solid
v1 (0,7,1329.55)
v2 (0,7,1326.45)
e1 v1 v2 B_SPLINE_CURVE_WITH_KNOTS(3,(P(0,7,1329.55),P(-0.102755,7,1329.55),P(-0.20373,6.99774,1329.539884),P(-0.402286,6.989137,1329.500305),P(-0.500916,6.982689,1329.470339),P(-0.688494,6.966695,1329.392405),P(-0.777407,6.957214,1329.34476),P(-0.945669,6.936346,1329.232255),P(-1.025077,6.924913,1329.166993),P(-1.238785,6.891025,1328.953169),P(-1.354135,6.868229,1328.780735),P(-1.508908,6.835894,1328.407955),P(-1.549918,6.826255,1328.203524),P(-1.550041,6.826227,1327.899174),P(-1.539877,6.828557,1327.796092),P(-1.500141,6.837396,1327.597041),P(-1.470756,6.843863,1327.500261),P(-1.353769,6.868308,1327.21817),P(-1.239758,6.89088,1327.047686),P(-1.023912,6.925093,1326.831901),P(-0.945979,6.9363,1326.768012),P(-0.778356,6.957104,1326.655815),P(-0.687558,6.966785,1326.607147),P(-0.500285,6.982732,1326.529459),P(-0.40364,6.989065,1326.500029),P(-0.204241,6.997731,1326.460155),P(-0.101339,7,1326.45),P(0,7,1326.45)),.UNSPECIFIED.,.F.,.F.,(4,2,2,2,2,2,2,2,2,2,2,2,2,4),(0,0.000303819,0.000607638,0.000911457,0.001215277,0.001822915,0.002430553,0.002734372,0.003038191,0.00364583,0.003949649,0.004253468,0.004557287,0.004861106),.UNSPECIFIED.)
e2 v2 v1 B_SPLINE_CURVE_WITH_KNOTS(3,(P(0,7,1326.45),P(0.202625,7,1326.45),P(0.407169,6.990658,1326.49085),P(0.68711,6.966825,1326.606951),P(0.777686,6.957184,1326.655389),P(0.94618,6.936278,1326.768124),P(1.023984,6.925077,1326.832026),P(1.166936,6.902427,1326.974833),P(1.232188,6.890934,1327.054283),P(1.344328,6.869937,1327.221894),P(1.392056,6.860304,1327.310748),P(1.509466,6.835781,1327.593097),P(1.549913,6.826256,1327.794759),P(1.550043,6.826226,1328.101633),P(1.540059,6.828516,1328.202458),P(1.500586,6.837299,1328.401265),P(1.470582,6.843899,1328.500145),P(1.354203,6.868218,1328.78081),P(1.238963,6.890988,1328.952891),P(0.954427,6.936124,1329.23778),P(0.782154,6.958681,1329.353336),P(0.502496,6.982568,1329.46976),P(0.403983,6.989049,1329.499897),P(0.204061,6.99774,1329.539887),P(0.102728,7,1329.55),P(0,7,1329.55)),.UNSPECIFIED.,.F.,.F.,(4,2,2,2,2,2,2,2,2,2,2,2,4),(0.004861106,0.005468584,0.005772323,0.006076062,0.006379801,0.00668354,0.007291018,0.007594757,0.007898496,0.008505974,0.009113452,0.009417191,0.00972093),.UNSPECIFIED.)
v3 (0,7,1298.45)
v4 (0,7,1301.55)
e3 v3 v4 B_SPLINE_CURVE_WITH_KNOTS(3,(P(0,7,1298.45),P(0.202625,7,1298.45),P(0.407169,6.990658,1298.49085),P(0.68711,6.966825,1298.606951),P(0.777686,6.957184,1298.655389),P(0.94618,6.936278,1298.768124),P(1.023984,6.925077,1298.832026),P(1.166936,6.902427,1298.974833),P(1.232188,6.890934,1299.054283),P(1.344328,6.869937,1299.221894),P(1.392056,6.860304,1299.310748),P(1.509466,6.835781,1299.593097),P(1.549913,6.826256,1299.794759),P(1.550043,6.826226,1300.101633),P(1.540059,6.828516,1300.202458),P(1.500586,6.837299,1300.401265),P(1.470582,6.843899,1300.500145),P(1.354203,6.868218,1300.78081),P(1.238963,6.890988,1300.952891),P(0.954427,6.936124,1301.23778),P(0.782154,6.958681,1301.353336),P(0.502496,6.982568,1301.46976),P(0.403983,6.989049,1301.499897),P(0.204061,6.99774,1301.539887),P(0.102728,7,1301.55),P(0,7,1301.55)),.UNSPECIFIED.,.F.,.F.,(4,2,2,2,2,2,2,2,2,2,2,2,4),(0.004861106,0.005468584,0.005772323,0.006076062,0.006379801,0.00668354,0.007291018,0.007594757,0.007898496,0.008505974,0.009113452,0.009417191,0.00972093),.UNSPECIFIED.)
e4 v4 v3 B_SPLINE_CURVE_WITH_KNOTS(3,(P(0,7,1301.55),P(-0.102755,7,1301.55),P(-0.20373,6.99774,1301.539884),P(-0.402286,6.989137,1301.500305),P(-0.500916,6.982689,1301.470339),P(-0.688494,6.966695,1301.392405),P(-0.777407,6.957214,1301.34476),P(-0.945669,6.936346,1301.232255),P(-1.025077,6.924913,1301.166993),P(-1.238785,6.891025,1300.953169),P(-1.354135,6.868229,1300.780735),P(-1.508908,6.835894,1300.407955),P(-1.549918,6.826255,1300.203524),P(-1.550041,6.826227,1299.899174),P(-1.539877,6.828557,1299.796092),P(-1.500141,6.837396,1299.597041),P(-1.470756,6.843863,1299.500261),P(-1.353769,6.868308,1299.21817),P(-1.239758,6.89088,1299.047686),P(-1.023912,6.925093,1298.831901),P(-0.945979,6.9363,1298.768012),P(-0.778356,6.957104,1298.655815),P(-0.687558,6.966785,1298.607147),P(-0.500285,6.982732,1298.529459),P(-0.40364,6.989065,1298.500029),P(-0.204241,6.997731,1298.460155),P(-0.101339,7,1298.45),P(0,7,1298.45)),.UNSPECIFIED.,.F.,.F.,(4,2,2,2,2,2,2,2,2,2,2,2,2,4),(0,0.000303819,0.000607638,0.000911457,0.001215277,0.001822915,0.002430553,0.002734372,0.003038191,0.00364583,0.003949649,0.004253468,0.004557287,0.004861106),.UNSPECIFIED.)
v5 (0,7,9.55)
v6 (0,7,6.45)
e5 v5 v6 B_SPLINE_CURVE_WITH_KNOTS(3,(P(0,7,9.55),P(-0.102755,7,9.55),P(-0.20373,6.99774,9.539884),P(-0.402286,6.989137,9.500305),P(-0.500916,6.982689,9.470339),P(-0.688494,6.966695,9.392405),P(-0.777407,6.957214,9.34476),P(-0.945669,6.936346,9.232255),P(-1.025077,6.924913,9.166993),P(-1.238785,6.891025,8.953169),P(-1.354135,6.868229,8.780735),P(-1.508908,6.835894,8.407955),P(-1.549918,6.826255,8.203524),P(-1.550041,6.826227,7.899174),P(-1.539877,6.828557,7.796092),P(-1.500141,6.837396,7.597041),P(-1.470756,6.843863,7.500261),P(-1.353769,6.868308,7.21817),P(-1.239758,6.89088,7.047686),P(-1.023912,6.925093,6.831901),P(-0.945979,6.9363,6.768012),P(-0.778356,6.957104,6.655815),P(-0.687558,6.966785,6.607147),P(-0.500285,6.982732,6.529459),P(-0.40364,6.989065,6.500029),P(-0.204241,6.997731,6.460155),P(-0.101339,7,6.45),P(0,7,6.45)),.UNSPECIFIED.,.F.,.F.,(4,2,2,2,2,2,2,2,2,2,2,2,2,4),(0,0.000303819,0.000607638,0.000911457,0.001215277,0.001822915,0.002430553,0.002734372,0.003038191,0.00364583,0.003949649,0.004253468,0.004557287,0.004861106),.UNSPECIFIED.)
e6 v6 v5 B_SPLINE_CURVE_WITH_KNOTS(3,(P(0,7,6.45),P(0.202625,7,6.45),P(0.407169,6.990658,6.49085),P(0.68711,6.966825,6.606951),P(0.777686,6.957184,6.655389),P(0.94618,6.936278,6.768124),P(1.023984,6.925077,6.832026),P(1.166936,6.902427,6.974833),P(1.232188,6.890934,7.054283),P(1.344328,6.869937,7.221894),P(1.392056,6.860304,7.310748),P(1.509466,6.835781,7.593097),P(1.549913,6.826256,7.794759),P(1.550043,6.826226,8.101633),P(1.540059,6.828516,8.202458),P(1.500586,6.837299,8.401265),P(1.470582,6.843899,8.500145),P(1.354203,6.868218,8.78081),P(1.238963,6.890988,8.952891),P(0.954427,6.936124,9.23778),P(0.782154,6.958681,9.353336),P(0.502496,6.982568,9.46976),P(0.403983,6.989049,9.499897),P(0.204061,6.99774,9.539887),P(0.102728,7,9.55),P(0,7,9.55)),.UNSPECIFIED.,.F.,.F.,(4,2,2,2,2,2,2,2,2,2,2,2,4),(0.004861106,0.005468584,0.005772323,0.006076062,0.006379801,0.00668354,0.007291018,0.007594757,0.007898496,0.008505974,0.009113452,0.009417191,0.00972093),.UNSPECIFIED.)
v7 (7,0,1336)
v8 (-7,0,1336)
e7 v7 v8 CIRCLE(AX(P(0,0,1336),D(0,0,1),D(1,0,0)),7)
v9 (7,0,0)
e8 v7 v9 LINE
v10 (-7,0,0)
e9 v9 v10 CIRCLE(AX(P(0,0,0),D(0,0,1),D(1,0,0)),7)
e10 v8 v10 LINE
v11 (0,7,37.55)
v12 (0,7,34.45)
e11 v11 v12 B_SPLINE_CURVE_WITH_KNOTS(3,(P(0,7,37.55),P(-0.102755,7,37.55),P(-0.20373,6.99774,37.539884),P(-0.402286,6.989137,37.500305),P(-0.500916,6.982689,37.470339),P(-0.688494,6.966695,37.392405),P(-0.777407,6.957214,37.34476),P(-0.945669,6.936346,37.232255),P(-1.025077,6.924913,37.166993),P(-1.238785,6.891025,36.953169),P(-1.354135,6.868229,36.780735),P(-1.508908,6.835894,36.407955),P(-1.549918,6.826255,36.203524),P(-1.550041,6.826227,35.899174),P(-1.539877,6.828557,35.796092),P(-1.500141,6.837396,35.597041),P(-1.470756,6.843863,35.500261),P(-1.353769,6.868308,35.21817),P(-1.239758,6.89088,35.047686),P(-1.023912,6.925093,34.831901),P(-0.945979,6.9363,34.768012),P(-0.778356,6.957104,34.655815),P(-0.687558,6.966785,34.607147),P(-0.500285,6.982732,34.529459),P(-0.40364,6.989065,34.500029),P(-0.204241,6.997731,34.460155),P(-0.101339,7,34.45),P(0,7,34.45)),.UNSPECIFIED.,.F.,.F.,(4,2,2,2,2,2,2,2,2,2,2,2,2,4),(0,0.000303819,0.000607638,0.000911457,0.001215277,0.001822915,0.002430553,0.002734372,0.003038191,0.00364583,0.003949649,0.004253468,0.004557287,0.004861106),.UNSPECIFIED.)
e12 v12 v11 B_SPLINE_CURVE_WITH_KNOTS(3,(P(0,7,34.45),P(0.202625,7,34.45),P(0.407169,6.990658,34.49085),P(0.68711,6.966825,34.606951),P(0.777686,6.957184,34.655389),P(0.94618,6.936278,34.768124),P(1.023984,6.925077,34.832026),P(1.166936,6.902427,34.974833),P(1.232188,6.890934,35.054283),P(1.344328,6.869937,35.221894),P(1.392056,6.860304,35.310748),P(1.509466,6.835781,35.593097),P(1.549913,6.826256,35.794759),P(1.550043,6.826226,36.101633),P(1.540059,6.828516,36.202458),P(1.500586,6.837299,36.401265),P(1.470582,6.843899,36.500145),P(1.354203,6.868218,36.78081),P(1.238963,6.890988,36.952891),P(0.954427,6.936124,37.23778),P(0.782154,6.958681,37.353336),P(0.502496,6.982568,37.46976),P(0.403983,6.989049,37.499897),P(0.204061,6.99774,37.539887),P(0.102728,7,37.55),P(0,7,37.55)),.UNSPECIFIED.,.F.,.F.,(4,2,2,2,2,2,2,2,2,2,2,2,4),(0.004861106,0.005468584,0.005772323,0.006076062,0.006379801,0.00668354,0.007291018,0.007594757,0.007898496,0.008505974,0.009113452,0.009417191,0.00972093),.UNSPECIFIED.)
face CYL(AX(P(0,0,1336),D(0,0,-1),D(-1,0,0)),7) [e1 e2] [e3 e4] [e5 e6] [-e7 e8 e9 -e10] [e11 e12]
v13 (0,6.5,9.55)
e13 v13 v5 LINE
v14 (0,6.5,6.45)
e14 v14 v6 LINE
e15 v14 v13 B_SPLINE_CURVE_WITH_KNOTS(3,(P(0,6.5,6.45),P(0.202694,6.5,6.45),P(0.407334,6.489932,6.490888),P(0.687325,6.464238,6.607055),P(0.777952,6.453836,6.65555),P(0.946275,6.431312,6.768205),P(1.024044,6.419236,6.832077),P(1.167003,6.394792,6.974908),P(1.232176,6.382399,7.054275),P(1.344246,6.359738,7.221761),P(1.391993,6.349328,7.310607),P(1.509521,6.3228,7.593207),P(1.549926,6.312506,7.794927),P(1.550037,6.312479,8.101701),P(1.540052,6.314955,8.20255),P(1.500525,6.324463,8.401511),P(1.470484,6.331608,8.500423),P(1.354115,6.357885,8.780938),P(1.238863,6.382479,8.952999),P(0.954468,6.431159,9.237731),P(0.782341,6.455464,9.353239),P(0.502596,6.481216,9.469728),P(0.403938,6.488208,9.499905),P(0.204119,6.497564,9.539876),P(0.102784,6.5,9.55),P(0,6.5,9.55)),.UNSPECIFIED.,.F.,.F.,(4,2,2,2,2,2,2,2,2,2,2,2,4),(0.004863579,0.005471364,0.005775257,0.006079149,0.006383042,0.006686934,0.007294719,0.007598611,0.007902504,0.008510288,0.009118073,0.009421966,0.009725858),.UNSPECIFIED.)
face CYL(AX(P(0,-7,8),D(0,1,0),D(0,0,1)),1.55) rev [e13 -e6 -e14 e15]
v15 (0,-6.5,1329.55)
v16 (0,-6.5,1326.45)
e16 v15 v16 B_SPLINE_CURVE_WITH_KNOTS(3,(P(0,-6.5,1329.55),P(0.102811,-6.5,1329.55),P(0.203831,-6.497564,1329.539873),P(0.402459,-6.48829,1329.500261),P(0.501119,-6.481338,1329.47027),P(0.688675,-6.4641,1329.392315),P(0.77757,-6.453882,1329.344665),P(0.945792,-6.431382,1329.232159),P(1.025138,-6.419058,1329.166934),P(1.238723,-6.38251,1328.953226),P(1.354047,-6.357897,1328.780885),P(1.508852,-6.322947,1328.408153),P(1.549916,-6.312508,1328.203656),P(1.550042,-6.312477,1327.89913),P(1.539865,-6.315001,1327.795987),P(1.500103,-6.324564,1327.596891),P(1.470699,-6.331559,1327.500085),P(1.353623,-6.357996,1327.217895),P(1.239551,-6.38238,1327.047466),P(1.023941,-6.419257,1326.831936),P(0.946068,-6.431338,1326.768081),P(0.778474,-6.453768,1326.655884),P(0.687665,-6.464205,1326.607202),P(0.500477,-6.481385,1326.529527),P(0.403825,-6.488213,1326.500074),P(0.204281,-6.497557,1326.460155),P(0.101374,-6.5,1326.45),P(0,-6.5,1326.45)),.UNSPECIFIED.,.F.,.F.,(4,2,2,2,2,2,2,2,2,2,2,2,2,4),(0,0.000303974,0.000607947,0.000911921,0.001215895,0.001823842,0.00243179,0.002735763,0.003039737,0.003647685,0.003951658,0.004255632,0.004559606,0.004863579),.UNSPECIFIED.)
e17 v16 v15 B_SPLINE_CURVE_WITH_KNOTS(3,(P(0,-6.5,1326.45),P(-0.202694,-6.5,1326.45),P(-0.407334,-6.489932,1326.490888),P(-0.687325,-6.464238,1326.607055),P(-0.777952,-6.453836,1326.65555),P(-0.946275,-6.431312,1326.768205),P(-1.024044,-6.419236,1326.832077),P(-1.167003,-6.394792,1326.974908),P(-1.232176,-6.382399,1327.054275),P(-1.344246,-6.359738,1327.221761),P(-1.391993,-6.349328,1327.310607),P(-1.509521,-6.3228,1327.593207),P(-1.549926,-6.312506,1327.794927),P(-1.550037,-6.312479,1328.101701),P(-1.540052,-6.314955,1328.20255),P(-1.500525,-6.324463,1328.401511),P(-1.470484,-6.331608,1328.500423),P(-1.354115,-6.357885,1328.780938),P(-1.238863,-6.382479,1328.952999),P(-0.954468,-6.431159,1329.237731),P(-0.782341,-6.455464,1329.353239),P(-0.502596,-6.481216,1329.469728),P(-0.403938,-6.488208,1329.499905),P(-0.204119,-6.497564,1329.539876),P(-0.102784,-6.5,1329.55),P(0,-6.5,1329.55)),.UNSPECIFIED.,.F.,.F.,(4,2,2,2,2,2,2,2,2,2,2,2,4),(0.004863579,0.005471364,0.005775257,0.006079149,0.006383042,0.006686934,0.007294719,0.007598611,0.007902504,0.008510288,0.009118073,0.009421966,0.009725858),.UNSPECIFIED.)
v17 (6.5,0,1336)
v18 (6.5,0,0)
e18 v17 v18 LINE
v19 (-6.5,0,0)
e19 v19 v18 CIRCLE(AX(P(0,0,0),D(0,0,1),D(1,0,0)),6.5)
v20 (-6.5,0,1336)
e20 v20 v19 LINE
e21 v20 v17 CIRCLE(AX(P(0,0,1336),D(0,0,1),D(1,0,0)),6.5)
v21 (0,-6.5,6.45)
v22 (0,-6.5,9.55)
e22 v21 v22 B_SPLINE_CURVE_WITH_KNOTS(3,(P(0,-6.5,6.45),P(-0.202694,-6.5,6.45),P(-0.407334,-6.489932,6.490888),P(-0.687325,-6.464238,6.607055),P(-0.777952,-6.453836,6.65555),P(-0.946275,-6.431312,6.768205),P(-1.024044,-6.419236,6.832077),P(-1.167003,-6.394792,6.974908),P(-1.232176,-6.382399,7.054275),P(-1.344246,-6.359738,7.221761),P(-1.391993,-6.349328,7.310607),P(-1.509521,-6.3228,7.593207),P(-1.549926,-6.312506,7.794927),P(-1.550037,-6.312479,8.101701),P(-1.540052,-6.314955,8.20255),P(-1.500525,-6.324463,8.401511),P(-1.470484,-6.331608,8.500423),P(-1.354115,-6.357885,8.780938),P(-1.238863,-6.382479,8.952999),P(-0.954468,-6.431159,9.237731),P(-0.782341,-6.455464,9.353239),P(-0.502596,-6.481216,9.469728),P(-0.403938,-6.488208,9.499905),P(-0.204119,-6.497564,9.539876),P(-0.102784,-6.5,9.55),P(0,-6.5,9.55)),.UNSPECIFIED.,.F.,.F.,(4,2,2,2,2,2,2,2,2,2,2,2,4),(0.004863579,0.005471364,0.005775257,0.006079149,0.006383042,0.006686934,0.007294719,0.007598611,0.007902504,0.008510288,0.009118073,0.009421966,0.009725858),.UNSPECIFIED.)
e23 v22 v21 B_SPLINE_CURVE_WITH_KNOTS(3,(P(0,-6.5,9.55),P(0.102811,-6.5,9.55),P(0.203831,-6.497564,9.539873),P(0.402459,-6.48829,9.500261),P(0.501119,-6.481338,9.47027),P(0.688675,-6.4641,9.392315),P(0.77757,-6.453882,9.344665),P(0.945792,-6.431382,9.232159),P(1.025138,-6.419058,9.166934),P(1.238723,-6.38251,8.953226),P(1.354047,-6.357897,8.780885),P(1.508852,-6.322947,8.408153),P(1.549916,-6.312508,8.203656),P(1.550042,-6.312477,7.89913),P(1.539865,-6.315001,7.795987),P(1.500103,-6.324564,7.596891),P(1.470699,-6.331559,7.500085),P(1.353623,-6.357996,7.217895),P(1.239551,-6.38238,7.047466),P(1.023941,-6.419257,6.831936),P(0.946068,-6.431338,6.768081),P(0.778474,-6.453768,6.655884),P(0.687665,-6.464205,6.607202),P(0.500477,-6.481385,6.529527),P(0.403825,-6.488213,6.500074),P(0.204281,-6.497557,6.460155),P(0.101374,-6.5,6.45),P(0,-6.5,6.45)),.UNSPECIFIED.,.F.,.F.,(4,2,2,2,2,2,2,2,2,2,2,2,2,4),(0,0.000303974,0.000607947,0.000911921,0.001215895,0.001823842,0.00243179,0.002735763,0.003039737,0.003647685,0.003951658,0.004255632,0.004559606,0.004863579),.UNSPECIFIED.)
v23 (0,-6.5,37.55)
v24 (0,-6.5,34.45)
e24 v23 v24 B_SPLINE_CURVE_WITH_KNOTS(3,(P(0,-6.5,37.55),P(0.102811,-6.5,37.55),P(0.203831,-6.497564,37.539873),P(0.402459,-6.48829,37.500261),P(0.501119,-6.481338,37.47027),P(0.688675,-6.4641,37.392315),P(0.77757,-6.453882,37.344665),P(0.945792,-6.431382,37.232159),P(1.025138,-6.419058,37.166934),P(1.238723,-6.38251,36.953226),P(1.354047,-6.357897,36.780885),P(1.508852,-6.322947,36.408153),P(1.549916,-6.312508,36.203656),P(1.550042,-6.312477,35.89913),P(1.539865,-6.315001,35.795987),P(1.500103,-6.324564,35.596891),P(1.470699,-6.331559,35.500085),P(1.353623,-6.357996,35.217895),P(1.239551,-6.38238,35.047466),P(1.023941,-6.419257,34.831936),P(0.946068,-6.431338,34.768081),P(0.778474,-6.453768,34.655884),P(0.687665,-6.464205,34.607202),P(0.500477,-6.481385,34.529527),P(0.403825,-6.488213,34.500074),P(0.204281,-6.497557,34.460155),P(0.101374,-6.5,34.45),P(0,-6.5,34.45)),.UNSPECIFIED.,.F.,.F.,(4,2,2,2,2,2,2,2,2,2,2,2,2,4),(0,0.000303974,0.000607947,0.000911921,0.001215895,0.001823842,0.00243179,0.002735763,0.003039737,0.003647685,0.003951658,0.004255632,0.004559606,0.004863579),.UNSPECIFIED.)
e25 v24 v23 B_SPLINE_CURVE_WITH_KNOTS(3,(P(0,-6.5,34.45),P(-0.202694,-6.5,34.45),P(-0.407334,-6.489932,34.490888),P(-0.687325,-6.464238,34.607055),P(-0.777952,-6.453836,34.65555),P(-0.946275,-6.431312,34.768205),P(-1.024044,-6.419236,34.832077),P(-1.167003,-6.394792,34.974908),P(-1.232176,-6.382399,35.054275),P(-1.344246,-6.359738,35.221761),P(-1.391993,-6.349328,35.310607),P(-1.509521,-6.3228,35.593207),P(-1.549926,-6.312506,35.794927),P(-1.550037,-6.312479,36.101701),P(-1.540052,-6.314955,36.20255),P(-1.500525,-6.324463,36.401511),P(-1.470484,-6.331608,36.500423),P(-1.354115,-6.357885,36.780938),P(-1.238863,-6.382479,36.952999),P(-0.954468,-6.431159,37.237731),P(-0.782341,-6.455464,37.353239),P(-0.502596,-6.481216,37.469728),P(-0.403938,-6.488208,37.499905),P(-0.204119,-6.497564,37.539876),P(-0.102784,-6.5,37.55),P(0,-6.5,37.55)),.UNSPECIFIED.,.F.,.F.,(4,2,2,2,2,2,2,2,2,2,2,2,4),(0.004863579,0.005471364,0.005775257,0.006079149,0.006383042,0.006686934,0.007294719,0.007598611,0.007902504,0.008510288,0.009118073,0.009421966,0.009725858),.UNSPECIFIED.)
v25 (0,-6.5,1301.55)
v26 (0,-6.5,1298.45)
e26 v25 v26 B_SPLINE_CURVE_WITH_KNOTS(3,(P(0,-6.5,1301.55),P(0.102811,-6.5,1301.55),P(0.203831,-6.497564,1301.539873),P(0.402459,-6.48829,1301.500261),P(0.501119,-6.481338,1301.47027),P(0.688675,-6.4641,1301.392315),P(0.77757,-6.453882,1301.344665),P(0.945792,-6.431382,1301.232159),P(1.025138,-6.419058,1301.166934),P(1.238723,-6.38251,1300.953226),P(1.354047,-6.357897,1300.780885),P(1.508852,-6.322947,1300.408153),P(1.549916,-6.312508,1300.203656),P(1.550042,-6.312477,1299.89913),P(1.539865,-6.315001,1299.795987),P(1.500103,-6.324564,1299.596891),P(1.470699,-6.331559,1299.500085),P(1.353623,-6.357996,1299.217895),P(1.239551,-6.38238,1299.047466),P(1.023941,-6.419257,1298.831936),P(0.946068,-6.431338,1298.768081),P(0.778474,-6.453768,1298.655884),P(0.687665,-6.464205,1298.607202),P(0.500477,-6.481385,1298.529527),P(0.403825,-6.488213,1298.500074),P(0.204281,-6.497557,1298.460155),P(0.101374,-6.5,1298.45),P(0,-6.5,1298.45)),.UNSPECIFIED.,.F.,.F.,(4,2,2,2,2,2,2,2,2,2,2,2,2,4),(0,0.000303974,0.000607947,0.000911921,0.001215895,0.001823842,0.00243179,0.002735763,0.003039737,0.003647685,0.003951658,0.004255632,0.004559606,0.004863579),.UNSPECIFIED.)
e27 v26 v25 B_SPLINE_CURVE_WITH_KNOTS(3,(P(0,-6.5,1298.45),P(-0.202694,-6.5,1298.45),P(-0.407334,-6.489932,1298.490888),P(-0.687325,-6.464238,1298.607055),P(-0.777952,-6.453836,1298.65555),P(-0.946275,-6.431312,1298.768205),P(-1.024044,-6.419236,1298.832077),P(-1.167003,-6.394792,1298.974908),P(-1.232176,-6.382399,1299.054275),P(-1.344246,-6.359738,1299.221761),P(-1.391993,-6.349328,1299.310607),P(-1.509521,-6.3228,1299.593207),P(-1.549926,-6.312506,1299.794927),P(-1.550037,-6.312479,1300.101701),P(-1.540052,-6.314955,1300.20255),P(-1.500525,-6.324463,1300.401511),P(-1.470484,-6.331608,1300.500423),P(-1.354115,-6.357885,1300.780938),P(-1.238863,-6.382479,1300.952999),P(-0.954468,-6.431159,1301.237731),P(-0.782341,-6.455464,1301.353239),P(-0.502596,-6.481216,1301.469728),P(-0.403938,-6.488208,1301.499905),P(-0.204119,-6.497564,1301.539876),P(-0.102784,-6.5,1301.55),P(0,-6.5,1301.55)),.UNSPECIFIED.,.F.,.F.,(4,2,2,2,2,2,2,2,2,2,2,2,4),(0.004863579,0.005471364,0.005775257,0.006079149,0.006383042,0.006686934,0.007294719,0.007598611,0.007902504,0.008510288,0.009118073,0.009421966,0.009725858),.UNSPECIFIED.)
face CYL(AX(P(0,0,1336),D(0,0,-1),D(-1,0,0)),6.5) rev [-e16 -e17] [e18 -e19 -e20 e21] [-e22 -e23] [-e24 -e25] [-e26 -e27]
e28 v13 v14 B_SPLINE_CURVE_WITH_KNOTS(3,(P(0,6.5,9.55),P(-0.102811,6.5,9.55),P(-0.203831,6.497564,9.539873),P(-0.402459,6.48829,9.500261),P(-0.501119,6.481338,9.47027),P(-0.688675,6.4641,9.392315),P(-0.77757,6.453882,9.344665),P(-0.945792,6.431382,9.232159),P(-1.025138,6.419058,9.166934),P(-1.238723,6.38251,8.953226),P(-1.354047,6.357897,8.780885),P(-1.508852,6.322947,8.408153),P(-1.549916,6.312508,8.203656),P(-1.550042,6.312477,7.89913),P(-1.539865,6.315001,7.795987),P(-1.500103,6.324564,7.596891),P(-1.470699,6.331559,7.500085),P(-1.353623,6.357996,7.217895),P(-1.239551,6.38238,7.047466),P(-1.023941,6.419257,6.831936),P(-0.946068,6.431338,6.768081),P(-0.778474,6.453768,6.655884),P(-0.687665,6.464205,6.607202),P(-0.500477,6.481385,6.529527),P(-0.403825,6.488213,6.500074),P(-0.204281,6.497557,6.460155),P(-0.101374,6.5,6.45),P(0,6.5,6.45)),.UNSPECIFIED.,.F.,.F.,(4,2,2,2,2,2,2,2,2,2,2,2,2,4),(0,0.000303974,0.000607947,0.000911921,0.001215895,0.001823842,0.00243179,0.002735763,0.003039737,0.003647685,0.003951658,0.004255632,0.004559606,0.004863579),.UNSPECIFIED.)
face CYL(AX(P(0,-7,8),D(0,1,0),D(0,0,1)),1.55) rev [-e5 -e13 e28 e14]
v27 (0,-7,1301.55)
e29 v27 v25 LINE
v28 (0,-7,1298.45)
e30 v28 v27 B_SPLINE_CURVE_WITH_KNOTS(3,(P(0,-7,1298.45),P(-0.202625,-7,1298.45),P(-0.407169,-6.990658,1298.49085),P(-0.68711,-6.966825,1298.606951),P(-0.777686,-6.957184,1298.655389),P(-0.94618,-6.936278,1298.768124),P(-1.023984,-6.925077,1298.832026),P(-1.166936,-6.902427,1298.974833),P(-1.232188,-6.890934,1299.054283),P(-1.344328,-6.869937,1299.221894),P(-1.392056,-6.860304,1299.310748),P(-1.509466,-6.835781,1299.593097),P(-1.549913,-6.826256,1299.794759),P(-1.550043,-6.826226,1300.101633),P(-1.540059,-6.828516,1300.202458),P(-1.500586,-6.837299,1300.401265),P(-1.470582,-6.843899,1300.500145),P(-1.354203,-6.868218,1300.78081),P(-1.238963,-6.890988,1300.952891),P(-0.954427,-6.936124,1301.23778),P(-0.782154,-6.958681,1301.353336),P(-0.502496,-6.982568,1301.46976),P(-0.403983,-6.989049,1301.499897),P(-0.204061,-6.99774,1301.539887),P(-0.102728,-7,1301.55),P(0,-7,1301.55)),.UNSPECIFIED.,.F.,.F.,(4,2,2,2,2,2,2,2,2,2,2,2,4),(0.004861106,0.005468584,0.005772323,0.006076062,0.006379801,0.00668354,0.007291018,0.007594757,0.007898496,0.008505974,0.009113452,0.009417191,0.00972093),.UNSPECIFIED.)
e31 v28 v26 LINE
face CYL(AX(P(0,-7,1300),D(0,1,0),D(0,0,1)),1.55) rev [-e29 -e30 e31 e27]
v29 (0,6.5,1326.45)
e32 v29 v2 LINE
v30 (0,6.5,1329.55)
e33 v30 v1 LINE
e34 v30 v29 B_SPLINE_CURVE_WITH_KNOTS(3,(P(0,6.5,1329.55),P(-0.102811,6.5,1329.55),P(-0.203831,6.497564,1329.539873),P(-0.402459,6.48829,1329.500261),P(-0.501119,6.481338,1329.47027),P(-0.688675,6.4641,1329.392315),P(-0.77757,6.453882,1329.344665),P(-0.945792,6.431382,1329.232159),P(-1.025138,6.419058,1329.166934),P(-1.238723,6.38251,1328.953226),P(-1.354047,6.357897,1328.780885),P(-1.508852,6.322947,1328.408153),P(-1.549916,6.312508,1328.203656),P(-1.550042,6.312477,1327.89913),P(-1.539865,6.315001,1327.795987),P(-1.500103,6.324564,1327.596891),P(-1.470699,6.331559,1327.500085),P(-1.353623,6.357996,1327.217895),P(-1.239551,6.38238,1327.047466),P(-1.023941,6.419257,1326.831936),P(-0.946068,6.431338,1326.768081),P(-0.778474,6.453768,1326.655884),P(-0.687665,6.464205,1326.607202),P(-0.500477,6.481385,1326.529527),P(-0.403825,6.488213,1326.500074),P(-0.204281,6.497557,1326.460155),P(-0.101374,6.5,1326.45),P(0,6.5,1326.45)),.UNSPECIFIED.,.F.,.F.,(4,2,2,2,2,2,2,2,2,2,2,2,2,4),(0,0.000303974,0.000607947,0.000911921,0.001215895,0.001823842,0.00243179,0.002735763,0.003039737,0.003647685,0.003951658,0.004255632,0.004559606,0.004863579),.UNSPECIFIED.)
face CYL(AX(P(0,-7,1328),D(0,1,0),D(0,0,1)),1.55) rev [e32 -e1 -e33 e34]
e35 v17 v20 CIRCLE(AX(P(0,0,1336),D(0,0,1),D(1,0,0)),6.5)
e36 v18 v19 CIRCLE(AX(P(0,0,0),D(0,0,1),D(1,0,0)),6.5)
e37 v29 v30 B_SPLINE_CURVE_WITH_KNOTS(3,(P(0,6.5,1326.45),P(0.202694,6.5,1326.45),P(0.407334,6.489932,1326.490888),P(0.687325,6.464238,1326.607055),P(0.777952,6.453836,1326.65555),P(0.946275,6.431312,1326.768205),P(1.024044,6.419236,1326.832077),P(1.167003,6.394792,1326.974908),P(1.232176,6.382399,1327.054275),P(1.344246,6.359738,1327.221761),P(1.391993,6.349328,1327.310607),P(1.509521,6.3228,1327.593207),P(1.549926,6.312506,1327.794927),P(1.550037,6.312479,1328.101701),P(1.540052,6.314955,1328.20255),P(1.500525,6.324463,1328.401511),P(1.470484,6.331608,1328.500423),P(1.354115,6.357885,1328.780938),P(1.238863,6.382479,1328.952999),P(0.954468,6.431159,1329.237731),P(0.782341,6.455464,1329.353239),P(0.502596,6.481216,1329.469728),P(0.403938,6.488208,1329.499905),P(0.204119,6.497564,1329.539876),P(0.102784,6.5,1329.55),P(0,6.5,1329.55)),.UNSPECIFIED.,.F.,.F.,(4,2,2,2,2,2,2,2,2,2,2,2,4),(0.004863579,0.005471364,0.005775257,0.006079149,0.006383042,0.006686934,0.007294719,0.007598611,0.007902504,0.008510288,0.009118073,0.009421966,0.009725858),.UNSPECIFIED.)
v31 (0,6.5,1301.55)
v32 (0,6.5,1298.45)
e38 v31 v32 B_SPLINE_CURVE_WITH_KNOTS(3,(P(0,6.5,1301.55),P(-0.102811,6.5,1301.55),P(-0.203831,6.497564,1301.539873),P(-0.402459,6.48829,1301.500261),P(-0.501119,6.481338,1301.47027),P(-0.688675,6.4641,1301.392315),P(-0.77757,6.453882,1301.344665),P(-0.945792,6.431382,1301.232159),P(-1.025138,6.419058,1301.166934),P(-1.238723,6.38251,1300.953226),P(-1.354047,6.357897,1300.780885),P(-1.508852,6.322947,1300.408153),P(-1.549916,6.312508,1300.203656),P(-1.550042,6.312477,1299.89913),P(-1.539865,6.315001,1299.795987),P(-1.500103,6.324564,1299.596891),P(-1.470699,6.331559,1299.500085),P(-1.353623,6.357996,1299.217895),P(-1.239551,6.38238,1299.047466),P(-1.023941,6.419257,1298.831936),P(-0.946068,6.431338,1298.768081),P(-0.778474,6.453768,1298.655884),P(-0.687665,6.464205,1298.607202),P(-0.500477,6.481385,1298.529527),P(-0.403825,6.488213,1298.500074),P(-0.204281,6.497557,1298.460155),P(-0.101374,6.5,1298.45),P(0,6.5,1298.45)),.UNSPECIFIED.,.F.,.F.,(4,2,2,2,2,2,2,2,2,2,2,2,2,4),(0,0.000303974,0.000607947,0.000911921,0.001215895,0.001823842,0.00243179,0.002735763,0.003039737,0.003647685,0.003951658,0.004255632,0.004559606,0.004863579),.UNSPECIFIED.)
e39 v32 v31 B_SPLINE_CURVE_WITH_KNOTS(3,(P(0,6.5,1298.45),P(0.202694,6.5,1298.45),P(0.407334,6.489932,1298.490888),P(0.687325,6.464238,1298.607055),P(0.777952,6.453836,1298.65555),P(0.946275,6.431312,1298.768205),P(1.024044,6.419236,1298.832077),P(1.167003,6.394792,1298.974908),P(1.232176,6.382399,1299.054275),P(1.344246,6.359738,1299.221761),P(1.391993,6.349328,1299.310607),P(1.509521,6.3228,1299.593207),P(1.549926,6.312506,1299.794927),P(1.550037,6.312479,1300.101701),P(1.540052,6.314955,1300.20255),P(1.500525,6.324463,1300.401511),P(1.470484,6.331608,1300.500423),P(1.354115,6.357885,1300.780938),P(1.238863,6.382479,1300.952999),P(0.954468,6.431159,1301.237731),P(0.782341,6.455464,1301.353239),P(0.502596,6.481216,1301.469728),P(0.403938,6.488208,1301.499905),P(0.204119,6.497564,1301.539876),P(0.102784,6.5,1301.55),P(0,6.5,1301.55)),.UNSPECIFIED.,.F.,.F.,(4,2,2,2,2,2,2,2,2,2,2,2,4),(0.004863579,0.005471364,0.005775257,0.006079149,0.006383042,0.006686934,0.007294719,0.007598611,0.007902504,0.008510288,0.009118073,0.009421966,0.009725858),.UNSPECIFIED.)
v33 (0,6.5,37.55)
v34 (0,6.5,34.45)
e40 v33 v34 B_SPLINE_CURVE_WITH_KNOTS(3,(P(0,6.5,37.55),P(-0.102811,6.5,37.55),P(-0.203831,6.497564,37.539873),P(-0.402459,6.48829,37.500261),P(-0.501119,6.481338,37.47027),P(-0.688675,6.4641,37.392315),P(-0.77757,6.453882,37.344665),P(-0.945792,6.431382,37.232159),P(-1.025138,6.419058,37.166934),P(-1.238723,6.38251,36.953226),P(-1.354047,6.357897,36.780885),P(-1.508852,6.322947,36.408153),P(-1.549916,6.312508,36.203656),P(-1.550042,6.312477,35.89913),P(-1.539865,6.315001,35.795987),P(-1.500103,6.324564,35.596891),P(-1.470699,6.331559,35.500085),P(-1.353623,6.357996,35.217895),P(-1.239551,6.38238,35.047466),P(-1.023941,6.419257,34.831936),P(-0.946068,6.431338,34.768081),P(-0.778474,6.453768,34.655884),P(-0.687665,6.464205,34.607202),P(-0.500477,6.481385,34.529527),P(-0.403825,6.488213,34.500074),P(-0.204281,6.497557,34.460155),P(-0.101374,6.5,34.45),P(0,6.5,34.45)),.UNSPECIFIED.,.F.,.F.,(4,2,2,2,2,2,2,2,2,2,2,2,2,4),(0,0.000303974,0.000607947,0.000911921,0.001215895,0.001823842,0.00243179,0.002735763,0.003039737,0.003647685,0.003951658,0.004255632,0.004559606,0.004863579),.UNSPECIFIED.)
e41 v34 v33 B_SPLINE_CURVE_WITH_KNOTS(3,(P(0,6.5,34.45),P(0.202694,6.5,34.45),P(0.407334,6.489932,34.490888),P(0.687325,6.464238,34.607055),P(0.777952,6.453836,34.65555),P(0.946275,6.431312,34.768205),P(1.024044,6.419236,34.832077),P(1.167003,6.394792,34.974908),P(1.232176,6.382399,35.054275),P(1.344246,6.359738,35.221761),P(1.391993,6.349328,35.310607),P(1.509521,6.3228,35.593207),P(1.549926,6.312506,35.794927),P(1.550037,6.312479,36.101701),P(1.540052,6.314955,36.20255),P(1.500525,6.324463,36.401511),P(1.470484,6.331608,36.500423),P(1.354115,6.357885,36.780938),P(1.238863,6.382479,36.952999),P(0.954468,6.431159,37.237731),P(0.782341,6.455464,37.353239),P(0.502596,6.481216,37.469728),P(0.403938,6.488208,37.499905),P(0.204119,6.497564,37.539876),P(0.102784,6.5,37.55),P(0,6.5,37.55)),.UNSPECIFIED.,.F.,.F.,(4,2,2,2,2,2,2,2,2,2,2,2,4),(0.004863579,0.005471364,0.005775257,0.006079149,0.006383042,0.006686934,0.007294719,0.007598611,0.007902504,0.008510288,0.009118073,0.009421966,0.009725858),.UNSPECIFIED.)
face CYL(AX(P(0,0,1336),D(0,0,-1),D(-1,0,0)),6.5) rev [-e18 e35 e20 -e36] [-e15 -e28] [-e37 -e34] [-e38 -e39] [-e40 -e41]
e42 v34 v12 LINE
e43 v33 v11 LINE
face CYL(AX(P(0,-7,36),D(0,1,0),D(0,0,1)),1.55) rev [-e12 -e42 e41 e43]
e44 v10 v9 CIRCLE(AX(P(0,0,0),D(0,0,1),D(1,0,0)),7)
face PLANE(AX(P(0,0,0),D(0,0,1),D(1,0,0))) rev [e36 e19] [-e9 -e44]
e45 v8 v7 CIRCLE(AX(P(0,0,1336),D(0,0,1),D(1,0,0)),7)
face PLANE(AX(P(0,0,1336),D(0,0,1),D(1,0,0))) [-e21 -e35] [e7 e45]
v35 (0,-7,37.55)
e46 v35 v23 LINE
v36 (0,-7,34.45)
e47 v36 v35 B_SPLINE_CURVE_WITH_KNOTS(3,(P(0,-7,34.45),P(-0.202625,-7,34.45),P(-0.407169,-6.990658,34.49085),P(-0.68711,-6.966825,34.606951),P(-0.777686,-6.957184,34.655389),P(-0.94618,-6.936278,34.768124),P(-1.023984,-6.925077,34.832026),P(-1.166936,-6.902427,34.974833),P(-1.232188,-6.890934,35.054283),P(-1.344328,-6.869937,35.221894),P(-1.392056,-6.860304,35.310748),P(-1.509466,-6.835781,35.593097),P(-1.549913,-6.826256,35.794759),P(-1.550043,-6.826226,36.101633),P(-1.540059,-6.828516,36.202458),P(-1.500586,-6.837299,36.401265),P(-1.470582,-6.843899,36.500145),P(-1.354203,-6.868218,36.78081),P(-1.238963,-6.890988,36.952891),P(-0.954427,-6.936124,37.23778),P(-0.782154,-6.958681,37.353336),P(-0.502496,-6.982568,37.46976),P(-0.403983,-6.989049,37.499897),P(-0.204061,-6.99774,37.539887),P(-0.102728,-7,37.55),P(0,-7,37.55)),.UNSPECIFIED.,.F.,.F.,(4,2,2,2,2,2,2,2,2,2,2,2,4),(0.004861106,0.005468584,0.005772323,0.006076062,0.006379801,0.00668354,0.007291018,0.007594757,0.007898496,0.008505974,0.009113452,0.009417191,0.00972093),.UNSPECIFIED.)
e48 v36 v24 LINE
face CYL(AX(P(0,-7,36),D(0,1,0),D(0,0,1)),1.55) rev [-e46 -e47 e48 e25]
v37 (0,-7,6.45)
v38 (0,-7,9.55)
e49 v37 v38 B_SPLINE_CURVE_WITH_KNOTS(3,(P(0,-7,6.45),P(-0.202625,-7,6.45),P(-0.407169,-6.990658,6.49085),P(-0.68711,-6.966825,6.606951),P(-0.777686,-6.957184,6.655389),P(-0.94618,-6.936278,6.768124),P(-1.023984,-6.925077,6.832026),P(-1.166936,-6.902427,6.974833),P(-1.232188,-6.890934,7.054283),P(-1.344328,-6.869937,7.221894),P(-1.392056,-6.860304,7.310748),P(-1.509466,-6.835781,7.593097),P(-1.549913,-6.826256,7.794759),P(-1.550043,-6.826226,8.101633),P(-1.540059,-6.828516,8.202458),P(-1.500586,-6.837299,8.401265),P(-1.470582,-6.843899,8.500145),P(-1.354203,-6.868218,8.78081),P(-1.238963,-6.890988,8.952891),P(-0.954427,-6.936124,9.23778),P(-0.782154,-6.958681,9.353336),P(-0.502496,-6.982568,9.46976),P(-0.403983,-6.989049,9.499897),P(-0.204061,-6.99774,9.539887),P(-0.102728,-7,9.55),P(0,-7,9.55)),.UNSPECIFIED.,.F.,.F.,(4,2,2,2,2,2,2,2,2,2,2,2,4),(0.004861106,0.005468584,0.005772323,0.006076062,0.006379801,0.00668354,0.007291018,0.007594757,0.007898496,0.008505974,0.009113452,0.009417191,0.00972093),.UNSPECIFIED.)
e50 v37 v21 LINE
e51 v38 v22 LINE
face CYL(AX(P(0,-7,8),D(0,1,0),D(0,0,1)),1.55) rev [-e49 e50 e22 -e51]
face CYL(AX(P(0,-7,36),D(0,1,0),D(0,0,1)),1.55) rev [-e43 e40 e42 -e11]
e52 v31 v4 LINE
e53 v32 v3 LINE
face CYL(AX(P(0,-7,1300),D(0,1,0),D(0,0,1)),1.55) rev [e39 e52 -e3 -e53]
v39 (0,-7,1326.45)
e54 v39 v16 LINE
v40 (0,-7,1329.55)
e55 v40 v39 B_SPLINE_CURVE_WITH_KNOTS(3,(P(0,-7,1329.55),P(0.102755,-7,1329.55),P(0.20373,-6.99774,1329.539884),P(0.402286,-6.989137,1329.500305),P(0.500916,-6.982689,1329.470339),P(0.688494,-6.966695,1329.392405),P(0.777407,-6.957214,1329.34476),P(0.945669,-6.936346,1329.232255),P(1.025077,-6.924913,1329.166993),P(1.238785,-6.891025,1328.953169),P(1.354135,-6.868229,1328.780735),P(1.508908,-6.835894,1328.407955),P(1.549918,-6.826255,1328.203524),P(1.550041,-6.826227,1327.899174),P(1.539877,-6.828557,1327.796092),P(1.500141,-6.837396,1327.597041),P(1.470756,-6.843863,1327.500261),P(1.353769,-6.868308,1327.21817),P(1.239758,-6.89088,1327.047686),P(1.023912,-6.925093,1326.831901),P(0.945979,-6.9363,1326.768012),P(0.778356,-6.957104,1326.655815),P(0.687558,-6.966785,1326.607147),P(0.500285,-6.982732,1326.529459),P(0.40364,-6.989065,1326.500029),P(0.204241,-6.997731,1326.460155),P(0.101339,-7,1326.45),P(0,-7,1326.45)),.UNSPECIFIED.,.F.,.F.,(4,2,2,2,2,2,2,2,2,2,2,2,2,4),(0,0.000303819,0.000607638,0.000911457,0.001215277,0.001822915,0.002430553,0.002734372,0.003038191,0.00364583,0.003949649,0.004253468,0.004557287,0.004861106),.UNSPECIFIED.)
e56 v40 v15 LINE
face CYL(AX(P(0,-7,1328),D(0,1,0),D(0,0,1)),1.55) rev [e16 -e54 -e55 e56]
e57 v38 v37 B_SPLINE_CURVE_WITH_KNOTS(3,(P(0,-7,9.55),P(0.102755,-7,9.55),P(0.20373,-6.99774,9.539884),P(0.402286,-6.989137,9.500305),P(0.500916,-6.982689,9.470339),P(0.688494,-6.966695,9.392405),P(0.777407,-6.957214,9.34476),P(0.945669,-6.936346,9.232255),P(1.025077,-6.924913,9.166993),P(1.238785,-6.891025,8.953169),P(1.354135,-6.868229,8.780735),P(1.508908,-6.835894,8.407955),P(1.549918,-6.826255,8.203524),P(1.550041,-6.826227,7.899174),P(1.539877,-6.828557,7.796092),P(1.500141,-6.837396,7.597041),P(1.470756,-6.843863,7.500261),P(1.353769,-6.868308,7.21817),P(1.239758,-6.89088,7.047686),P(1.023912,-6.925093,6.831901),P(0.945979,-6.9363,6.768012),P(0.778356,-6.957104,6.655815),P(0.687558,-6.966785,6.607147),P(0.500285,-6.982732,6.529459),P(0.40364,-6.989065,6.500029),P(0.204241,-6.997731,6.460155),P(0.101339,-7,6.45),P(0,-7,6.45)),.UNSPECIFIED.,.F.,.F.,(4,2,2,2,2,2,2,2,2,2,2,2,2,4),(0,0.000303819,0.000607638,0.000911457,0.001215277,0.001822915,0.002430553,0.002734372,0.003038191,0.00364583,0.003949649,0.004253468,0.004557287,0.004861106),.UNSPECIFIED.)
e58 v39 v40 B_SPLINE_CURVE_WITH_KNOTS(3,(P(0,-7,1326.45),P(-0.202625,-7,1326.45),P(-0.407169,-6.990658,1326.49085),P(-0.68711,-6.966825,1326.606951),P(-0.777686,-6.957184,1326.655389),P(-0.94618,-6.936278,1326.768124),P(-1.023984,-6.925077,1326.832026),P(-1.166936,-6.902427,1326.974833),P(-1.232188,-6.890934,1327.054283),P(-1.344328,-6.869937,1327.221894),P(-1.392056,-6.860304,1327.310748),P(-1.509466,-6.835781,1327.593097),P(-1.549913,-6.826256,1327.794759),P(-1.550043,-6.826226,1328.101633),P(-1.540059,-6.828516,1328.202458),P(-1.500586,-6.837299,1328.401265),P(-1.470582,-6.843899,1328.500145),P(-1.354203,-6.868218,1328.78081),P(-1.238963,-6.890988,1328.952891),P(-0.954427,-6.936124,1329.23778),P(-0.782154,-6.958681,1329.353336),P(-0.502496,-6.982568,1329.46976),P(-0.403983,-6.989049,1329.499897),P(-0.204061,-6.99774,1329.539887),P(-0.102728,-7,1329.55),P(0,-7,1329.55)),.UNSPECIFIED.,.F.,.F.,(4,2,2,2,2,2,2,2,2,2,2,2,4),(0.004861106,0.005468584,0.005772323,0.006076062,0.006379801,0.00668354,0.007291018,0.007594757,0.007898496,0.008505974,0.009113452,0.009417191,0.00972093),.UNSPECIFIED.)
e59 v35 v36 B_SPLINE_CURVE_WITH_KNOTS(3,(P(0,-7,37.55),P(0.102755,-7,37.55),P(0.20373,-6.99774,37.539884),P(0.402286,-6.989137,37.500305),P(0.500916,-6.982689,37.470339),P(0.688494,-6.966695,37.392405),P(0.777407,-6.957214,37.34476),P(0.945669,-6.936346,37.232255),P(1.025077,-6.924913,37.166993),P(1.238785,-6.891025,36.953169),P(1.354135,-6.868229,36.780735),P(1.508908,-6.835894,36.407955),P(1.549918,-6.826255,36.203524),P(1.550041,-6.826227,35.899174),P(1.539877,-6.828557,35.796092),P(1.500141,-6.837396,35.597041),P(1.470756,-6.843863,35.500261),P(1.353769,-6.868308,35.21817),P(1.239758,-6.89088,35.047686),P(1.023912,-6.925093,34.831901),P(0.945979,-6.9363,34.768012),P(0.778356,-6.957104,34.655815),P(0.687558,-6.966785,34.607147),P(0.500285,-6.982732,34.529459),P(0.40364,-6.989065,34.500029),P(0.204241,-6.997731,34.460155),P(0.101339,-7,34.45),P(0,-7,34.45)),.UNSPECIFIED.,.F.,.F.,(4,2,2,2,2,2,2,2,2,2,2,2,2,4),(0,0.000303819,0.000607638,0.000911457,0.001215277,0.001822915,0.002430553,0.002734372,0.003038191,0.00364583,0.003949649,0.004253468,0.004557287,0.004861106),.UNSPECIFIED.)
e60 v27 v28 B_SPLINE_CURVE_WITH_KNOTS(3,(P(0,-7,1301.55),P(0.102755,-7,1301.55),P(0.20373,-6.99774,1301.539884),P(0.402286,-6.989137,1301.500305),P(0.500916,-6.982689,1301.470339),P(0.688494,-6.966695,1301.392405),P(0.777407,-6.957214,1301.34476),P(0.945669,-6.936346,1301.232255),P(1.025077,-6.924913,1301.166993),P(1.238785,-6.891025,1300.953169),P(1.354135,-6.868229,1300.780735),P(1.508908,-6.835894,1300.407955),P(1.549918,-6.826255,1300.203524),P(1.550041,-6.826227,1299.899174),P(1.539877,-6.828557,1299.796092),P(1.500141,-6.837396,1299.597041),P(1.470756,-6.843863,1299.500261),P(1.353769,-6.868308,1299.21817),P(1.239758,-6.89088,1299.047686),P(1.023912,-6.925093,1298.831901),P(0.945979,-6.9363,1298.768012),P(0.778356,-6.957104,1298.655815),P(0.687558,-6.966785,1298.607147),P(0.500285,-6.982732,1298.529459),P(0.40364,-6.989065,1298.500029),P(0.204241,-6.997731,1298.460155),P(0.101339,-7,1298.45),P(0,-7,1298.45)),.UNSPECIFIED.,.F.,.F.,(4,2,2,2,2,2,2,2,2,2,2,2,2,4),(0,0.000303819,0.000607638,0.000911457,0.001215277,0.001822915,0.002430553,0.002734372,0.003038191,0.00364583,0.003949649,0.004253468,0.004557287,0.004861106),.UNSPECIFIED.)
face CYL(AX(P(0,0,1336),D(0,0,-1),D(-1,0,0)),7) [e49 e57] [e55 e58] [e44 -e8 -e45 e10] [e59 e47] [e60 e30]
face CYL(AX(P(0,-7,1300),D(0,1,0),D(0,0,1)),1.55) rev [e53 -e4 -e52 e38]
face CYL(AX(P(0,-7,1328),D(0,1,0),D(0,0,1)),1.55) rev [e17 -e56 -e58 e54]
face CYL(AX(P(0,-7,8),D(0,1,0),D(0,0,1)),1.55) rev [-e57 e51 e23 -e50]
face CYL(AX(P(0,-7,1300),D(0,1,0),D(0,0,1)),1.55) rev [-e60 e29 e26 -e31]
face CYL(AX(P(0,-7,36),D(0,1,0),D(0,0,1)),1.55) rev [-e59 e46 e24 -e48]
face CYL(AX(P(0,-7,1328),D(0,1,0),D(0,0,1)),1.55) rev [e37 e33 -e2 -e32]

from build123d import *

# Parameters (mm, degrees)
SKETCH_2_R               = 7
SKETCH_2_R_2             = 6.5
EXTRUDE_2_DEPTH          = 1336
CUT_EXTRUDE_1_DEPTH      = 1337.036676143
CUT_EXTRUDE_1_DEPTH_BACK = 1337.036676143
SKETCH_3_R               = 1.55


with BuildPart() as part:
    # 草图2 → 凸台-拉伸2 (new body)
    with BuildSketch(Plane.XY):
        with Locations(Location((0, 0, 0), (0, 0, 180))):
            Circle(SKETCH_2_R)
        with Locations(Location((0, 0, 0), (0, 0, 180))):
            Circle(SKETCH_2_R_2, mode=Mode.SUBTRACT)
    extrude(amount=EXTRUDE_2_DEPTH)

    # 草图3 → 切除-拉伸1 (cut, two sides: drawn at the far end of the back side and taken through both)
    with BuildSketch(Plane(origin=(0, 0, 0), x_dir=(1, 0, 0), z_dir=(0, 1, 0)).offset(-CUT_EXTRUDE_1_DEPTH_BACK)):
        with Locations(Location((0, -8, 0), (0, 0, 270))):
            Circle(SKETCH_3_R)
        with Locations(Location((0, -36, 0), (0, 0, 270))):
            Circle(SKETCH_3_R)
        with Locations(Location((0, -1328, 0), (0, 0, 270))):
            Circle(SKETCH_3_R)
        with Locations(Location((0, -1300, 0), (0, 0, 270))):
            Circle(SKETCH_3_R)
    extrude(amount=CUT_EXTRUDE_1_DEPTH + CUT_EXTRUDE_1_DEPTH_BACK, mode=Mode.SUBTRACT)


solid = part.part
